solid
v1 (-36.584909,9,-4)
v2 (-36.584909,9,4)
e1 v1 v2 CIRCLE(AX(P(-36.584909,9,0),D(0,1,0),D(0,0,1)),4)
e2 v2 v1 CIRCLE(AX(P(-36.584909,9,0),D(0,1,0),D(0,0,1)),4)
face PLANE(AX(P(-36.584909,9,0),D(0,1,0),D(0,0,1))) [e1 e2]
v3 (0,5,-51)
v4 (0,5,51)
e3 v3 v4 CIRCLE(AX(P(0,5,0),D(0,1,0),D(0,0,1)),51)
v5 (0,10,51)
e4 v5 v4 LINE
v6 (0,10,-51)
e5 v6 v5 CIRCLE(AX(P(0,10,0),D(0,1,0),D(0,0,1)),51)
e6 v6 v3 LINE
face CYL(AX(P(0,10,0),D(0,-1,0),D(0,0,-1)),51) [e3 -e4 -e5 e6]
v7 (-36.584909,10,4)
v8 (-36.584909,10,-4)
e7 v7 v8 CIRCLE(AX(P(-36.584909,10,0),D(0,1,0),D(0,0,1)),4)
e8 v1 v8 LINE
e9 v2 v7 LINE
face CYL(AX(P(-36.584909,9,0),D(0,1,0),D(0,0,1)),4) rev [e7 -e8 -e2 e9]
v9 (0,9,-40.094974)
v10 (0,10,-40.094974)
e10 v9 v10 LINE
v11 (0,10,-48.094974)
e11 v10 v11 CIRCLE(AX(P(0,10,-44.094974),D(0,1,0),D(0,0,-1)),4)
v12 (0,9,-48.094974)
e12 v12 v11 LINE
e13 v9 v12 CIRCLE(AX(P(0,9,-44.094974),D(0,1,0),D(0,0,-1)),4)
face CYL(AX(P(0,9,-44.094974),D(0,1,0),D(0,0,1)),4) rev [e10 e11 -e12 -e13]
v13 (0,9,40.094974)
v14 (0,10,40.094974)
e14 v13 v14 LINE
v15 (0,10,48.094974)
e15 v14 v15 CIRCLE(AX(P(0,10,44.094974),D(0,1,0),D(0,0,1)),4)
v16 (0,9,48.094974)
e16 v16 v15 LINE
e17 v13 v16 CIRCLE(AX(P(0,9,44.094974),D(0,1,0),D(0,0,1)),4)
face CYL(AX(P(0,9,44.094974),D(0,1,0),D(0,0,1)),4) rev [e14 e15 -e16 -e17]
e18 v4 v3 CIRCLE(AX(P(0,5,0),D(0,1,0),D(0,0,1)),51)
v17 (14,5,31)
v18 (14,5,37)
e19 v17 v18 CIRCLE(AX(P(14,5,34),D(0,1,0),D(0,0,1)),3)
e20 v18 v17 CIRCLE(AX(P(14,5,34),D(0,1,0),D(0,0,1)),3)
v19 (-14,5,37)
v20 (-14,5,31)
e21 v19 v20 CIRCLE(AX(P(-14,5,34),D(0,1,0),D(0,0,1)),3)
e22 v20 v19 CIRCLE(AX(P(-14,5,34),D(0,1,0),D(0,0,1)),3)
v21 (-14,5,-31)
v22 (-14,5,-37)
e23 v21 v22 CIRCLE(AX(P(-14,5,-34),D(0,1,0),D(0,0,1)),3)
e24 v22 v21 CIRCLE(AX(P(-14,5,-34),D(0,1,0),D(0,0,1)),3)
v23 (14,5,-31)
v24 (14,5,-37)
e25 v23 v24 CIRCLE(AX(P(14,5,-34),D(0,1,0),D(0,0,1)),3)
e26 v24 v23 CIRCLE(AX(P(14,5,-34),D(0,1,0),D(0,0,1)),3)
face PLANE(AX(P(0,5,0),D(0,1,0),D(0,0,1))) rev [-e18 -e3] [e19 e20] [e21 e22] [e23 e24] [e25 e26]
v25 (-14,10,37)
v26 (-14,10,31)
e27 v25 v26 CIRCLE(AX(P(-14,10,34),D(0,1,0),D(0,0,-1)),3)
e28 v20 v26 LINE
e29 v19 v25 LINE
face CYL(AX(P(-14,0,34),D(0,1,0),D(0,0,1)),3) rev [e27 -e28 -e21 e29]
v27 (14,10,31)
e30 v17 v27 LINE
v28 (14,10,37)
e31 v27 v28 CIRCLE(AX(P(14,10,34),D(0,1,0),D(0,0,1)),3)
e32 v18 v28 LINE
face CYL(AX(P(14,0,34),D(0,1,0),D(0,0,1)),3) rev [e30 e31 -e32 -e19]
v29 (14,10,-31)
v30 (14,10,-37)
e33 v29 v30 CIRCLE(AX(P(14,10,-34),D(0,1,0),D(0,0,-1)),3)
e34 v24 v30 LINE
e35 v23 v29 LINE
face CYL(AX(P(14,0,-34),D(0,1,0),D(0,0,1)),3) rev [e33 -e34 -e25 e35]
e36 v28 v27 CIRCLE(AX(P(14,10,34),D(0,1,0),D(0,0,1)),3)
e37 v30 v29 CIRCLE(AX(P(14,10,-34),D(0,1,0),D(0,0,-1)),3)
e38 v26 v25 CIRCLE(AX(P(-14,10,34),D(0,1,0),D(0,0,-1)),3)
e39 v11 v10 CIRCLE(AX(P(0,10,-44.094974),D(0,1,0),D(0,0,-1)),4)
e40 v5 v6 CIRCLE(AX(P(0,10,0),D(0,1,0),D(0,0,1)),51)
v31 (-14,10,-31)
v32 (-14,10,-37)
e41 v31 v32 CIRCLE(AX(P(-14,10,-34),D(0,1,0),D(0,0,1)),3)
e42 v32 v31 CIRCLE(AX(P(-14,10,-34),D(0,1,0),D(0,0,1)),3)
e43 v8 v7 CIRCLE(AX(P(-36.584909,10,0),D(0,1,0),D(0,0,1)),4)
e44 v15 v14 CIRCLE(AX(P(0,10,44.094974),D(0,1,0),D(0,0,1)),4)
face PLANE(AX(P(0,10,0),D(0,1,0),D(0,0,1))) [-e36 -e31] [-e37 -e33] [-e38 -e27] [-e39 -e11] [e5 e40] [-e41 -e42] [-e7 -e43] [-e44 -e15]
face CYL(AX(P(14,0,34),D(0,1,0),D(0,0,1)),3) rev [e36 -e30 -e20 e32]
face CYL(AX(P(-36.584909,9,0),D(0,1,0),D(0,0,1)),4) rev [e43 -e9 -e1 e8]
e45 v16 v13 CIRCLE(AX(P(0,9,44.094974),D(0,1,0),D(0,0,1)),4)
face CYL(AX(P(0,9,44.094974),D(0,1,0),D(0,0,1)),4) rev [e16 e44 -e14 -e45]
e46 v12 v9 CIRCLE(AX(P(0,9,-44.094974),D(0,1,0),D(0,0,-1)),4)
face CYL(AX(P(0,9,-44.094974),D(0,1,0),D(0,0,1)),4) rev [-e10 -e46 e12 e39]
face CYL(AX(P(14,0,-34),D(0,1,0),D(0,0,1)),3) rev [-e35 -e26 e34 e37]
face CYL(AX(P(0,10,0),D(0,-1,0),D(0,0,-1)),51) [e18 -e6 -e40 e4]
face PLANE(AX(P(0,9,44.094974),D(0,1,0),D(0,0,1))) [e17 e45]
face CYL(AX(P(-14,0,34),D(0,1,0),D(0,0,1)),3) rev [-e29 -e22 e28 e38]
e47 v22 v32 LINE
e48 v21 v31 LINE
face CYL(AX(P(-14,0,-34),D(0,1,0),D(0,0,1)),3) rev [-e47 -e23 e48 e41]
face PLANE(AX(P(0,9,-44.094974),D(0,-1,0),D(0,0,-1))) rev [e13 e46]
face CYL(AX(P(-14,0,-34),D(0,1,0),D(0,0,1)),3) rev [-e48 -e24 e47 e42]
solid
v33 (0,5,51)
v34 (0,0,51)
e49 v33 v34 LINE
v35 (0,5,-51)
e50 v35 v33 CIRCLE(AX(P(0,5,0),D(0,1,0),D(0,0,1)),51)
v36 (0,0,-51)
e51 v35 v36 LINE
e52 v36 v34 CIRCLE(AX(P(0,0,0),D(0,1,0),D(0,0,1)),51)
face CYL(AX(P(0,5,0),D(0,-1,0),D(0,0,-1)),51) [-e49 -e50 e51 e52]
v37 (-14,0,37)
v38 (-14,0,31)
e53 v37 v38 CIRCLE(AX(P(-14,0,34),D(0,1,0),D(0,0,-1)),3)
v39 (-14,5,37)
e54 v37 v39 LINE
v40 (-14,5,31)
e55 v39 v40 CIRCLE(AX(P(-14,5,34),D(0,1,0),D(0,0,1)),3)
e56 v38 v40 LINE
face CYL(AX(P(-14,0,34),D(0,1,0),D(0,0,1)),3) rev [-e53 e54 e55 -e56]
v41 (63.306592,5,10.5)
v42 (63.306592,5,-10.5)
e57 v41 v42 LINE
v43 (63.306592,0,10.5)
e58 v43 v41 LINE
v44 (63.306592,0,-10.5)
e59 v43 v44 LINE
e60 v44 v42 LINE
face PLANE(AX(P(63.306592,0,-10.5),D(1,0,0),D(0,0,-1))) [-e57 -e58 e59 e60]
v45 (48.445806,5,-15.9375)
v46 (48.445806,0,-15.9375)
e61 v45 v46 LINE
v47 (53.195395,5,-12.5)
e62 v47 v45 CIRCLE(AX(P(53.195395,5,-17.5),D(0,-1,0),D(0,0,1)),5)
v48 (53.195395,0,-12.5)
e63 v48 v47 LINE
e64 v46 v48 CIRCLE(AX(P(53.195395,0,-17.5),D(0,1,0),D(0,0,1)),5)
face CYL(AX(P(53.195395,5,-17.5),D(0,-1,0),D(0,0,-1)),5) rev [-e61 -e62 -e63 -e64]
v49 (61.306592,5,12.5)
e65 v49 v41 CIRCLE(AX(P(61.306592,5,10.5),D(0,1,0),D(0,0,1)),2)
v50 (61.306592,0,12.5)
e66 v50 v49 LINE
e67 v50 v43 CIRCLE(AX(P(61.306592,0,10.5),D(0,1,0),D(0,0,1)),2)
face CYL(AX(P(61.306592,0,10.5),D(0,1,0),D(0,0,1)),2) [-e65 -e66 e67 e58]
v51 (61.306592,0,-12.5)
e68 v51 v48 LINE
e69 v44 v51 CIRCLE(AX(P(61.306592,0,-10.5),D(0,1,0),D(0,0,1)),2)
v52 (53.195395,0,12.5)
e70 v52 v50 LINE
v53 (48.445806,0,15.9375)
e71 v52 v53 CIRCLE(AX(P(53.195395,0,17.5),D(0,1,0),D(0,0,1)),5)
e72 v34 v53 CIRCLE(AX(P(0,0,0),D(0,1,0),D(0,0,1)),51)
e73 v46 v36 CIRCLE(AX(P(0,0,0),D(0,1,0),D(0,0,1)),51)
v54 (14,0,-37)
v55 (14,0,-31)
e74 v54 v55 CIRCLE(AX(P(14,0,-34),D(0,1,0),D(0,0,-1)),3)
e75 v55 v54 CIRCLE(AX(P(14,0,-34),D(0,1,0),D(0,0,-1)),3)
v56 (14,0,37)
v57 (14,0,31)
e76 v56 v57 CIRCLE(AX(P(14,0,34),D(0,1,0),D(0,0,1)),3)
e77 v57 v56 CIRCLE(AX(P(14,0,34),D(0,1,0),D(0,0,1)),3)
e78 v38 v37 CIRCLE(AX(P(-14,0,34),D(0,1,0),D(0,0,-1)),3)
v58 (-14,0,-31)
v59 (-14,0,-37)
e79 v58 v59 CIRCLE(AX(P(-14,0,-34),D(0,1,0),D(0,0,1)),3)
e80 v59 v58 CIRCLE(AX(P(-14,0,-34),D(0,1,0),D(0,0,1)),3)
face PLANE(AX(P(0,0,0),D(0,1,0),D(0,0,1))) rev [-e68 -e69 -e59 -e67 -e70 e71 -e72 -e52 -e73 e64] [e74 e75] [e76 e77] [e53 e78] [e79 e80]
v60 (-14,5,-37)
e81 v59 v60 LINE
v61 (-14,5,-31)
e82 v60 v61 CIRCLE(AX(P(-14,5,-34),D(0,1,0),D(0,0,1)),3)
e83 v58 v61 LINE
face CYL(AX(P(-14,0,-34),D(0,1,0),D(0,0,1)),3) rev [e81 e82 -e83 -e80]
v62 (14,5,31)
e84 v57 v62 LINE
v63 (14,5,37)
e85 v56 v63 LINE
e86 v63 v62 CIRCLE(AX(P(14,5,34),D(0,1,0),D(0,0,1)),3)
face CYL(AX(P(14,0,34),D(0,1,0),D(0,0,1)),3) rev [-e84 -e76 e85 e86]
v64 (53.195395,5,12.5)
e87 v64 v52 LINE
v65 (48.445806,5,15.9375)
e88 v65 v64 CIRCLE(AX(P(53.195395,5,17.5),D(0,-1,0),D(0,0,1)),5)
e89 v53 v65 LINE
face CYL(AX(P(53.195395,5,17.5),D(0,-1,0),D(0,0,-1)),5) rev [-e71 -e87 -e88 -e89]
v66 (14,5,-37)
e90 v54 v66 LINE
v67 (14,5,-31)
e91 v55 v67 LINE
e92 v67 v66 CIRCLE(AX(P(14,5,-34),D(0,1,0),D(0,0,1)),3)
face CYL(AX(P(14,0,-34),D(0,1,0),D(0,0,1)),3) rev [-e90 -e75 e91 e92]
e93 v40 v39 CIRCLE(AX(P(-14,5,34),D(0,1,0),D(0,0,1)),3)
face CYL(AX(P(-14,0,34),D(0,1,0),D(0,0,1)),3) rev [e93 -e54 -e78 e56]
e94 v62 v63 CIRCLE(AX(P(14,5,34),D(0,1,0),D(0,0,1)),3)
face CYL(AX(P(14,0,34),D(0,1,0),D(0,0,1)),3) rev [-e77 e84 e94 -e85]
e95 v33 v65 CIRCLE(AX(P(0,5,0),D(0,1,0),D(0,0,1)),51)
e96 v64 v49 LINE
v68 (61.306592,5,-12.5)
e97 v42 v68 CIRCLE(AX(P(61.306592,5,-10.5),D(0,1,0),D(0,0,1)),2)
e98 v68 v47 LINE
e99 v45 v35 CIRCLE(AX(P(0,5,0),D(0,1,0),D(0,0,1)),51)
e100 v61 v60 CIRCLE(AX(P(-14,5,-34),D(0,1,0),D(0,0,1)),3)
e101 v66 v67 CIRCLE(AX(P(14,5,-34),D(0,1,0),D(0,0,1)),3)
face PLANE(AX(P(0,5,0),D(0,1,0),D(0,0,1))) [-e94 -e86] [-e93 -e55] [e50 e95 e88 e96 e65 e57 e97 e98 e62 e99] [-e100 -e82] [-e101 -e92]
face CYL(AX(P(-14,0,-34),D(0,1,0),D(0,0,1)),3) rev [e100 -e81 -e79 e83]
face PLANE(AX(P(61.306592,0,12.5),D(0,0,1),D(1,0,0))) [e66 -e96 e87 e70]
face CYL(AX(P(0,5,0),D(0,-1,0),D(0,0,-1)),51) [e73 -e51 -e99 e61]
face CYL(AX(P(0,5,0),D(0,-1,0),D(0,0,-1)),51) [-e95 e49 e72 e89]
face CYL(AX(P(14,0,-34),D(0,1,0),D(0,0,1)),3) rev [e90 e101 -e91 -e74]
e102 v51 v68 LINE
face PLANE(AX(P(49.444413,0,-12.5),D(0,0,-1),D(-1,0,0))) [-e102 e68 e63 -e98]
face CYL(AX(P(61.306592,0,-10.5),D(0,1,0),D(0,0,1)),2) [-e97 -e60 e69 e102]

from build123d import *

# Parameters (mm, degrees)
SKETCH1_R           = 51
BOSS_EXTRUDE1_DEPTH = 5
BOSS_EXTRUDE2_DEPTH = 5
FILLET1_R           = 5
SKETCH4_R           = 51
BOSS_EXTRUDE3_DEPTH = 5
SKETCH5_R           = 3
CUT_EXTRUDE1_DEPTH  = 82.906804649
SKETCH6_R           = 4
CUT_EXTRUDE2_DEPTH  = 1


with BuildPart() as part:
    # Sketch1 → Boss-Extrude1 (new body)
    with BuildSketch(Plane(origin=(0, 0, 0), x_dir=(1, 0, 0), z_dir=(0, 1, 0))):
        with Locations(Location((0, 0, 0), (0, 0, 270))):
            Circle(SKETCH1_R)
    extrude(amount=BOSS_EXTRUDE1_DEPTH)

    # Sketch3 → Boss-Extrude2 (add)
    with BuildSketch(Plane(origin=(0, 5, 0), x_dir=(1, 0, 0), z_dir=(0, 1, 0))):
        with BuildLine():
            Line((49.444413233, 12.5), (61.306592452, 12.5))
            ThreePointArc((61.306592452, 12.5), (62.720806014, 11.914213562), (63.306592452, 10.5))
            Line((63.306592452, 10.5), (63.306592452, -10.5))
            ThreePointArc((63.306592452, -10.5), (62.720806014, -11.914213562), (61.306592452, -12.5))
            Line((61.306592452, -12.5), (49.444413233, -12.5))
            Line((49.444413233, -12.5), (49.444413233, 12.5))
        make_face()
    extrude(amount=-BOSS_EXTRUDE2_DEPTH)

    # Fillet1
    fillet1_edges = [part.edges().sort_by_distance(p)[0] for p in [
        (49.444413233, 2.5, 12.5),
        (49.444413233, 2.5, -12.5),
    ]]
    fillet(fillet1_edges, radius=FILLET1_R)


with BuildPart() as body_2:
    # Sketch4 → Boss-Extrude3 (new body)
    with BuildSketch(Plane(origin=(0, 5, 0), x_dir=(1, 0, 0), z_dir=(0, 1, 0))):
        with Locations(Location((0, 0, 0), (0, 0, 270))):
            Circle(SKETCH4_R)
    extrude(amount=BOSS_EXTRUDE3_DEPTH)


with BuildPart() as cut_extrude1_tool:
    # Sketch5 → Cut-Extrude1 (new, through all)
    with BuildSketch(Plane(origin=(0, 10, 0), x_dir=(1, 0, 0), z_dir=(0, 1, 0))):
        with Locations(Location((-14, 34, 0), (0, 0, 270))):
            Circle(SKETCH5_R)
        with Locations(Location((14, 34, 0), (0, 0, 270))):
            Circle(SKETCH5_R)
        with Locations(Location((14, -34, 0), (0, 0, 270))):
            Circle(SKETCH5_R)
        with Locations(Location((-14, -34, 0), (0, 0, 270))):
            Circle(SKETCH5_R)
    extrude(amount=-CUT_EXTRUDE1_DEPTH)


with BuildPart() as part_1:
    add(part.part)

    # Cut-Extrude1: cut by cut_extrude1_tool
    add(cut_extrude1_tool.part, mode=Mode.SUBTRACT)


with BuildPart() as body_2_1:
    add(body_2.part)

    # Cut-Extrude1: cut by cut_extrude1_tool
    add(cut_extrude1_tool.part, mode=Mode.SUBTRACT)

    # Sketch6 → Cut-Extrude2 (cut)
    with BuildSketch(Plane(origin=(0, 10, 0), x_dir=(1, 0, 0), z_dir=(0, 1, 0))):
        with Locations(Location((-36.58490914, 0, 0), (0, 0, 270))):
            Circle(SKETCH6_R)
        with Locations(Location((0, -44.09497379, 0), (0, 0, 270))):
            Circle(SKETCH6_R)
        with Locations(Location((0, 44.09497379, 0), (0, 0, 90))):
            Circle(SKETCH6_R)
    extrude(amount=-CUT_EXTRUDE2_DEPTH, mode=Mode.SUBTRACT)


solid = Compound([part_1.part, body_2_1.part])
